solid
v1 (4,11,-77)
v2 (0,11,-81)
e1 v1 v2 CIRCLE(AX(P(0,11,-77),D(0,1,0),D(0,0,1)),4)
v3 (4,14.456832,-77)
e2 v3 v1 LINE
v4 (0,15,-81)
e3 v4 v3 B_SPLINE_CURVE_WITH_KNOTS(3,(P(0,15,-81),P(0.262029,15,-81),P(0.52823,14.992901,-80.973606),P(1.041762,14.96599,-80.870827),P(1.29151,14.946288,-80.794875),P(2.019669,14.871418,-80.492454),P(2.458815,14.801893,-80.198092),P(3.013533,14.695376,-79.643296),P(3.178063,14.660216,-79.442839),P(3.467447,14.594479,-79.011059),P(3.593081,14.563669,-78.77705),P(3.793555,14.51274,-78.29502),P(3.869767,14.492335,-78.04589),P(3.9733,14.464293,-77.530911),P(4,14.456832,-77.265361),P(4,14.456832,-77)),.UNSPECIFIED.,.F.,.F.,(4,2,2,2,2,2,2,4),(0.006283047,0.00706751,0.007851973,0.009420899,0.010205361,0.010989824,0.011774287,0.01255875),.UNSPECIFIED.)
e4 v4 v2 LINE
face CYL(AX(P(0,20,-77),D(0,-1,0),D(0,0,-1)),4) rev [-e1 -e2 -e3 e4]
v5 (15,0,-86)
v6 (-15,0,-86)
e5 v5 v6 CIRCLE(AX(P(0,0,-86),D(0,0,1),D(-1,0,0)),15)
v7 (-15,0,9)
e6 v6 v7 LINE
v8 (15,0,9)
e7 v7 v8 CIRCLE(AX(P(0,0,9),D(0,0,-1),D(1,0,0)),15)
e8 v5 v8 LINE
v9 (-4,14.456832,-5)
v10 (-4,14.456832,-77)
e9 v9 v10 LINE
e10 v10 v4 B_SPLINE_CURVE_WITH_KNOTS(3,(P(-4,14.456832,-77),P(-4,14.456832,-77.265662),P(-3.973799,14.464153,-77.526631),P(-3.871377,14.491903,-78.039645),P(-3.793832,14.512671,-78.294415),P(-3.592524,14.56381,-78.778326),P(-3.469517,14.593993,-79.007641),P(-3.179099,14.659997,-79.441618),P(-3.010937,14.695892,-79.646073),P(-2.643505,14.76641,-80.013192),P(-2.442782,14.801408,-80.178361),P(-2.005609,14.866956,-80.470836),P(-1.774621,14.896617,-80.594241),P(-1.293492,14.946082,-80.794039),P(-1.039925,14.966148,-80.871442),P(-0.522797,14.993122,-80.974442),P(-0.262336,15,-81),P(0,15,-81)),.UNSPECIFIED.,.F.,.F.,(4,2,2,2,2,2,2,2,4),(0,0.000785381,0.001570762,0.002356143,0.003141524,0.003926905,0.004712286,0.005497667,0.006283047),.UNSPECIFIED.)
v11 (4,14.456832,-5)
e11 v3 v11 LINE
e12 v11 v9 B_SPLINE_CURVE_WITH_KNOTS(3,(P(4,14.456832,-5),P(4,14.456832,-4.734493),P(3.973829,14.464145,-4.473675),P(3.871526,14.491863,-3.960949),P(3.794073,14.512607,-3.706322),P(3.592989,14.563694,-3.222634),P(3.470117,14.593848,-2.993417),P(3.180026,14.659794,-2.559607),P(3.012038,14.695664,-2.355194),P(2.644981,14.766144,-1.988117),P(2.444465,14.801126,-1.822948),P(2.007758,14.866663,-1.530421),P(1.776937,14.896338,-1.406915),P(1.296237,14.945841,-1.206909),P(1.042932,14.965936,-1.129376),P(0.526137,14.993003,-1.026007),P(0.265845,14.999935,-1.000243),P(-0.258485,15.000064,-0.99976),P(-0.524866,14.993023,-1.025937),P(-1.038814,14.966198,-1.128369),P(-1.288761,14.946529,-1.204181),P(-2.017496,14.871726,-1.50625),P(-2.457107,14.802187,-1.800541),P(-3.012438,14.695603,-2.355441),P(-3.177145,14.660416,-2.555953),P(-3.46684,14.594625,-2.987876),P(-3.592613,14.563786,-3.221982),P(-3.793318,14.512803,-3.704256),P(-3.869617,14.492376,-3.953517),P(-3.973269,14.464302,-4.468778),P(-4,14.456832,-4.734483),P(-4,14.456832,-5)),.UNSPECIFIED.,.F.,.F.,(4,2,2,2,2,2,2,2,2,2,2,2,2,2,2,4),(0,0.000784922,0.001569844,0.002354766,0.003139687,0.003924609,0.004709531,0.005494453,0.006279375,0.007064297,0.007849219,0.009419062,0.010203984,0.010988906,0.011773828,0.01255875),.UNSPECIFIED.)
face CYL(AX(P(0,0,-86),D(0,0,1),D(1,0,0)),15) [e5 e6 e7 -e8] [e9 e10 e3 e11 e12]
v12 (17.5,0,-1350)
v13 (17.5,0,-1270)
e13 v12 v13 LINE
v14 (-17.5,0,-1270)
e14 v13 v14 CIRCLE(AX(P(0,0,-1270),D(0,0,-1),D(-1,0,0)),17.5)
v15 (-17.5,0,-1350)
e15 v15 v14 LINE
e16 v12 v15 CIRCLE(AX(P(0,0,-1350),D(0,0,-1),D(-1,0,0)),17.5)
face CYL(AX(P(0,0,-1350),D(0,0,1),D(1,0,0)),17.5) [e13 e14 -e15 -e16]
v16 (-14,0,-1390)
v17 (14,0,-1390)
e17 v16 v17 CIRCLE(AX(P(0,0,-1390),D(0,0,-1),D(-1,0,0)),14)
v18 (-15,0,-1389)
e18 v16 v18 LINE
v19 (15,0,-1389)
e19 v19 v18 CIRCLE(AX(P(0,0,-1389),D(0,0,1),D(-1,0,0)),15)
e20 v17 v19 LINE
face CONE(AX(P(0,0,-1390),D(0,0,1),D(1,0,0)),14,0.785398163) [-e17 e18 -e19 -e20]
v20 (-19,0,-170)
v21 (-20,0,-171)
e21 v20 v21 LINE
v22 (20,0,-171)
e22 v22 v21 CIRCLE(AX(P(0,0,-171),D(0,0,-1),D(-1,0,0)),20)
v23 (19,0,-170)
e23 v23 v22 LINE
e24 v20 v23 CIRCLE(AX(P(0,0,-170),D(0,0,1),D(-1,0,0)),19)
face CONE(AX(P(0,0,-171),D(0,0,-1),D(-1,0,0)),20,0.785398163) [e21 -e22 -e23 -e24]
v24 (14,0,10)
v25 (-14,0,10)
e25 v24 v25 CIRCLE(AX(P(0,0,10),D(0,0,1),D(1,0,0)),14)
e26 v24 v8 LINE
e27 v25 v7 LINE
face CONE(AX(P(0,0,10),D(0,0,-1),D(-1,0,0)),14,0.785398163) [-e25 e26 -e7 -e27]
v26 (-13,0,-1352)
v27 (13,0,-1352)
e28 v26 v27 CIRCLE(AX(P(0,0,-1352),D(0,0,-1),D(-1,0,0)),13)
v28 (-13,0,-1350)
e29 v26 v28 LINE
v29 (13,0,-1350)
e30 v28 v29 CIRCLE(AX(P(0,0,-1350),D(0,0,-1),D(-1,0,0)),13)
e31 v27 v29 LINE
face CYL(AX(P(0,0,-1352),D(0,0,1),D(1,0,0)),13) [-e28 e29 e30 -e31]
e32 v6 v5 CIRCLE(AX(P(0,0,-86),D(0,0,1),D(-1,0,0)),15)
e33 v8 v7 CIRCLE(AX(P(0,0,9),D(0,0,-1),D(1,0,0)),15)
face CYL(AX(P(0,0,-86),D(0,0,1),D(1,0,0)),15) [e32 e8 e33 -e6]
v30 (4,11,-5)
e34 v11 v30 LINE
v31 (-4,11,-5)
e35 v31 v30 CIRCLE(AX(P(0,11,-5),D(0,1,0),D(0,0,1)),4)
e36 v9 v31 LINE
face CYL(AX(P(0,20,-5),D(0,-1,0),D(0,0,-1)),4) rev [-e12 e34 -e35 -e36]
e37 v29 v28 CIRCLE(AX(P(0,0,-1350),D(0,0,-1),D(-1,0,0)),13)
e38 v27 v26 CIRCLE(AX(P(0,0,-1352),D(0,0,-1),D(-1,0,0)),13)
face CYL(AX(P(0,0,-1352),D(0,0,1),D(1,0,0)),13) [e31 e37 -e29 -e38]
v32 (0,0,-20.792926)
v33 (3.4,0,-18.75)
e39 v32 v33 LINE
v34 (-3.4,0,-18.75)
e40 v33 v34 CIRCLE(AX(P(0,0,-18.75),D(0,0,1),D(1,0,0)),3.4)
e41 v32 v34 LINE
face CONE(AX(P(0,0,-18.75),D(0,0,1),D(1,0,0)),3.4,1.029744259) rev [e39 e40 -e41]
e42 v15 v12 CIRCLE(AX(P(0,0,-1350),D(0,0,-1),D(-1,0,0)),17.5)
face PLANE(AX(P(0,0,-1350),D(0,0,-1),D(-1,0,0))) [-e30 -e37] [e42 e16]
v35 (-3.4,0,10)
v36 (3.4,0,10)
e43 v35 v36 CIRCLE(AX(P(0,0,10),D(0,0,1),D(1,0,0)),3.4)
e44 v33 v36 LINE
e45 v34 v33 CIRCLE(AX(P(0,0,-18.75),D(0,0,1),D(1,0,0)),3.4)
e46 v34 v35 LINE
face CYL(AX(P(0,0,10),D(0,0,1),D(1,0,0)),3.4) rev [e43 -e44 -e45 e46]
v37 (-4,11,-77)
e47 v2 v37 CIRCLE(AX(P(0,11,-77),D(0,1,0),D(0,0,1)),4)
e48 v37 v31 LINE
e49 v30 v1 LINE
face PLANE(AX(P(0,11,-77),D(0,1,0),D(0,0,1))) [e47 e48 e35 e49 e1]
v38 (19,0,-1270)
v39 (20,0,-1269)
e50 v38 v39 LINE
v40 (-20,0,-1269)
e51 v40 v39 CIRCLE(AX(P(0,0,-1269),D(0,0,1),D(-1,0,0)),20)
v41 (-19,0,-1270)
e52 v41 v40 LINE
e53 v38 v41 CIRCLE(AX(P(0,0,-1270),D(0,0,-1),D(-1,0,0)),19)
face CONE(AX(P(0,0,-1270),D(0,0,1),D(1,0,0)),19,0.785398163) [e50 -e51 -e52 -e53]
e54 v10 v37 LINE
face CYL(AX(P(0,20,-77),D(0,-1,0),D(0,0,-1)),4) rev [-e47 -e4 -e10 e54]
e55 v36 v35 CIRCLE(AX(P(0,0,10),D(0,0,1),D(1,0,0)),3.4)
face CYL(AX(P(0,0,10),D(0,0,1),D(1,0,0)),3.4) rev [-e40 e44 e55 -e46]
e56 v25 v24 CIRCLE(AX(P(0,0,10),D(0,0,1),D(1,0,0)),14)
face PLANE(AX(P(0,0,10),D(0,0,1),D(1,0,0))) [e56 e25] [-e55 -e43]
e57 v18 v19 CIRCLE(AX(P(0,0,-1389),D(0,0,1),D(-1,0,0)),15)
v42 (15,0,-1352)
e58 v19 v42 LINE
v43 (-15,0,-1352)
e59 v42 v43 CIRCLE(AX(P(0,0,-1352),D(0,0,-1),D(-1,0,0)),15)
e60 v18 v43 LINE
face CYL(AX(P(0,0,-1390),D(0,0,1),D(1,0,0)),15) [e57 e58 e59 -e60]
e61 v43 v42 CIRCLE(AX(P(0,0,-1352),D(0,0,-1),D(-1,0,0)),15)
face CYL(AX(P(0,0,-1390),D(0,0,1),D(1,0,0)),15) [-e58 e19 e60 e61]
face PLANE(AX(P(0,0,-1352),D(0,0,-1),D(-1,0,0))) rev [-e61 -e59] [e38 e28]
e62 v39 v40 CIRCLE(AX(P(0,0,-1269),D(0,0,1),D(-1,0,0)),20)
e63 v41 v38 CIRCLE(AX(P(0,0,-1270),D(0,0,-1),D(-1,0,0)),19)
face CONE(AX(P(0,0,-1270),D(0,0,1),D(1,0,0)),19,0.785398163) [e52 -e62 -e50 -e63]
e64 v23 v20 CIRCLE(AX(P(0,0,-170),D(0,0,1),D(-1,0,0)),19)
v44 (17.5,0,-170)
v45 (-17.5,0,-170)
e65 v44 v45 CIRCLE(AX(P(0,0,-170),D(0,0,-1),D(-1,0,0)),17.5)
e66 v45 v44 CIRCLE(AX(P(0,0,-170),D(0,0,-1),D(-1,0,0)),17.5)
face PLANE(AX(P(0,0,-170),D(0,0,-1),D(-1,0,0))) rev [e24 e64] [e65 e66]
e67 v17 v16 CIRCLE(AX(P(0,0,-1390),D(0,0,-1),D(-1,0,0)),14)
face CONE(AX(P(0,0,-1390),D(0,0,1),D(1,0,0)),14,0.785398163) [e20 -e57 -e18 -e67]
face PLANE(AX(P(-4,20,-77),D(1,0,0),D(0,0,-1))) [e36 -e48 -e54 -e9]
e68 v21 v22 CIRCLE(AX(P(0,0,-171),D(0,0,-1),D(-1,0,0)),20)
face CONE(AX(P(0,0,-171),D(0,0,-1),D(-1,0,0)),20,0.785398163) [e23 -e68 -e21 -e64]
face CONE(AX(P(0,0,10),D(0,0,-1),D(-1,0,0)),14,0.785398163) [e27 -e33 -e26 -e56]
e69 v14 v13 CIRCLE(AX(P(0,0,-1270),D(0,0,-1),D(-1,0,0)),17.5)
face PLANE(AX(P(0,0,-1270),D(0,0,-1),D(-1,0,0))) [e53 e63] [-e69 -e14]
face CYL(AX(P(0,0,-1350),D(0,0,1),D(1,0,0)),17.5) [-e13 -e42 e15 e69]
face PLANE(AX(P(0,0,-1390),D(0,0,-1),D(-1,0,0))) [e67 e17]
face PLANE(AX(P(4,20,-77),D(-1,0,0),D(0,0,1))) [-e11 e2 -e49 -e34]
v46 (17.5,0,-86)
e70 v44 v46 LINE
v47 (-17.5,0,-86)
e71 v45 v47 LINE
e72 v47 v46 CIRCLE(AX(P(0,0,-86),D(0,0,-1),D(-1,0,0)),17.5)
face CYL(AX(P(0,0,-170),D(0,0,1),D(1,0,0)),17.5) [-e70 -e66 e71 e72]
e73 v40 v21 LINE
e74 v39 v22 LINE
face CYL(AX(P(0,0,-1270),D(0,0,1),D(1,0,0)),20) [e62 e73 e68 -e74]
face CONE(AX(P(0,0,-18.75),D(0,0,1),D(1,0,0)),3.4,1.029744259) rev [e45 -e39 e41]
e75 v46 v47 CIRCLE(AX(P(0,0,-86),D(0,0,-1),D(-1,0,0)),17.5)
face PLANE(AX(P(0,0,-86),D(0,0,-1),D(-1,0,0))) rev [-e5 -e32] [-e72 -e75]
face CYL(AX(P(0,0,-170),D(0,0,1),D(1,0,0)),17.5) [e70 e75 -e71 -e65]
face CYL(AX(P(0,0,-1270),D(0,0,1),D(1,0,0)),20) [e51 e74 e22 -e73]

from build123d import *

# Parameters (mm, degrees)
SKETCH_2_R             = 15
EXTRUDE_1_DEPTH        = 96
SKETCH_3_R             = 17.5
EXTRUDE_2_DEPTH        = 84
SKETCH_4_R             = 20
EXTRUDE_3_DEPTH        = 1100
SKETCH_6_R             = 17.5
EXTRUDE_4_DEPTH        = 80
SKETCH_7_R             = 13
EXTRUDE_5_DEPTH        = 2
SKETCH_9_R             = 15
EXTRUDE_6_DEPTH        = 38
CHAMFER_1_SIZE         = 1
CHAMFER_2_SIZE         = 1
CHAMFER_3_SIZE         = 1
CHAMFER_4_SIZE         = 1
HOLE_WIZARD_M8_2_D     = 6.8
HOLE_WIZARD_M8_2_DEPTH = 28.75
HOLE_WIZARD_M8_2_TIP   = 2.042926105
CUT_EXTRUDE_1_DEPTH    = 1391.489482161


with BuildPart() as part:
    # 草图2 → 凸台-拉伸1 (new body)
    with BuildSketch(Plane.XY):
        Circle(SKETCH_2_R)
    extrude(amount=-EXTRUDE_1_DEPTH)

    # 草图3 → 凸台-拉伸2 (add)
    with BuildSketch(Plane(origin=(0, 0, -96), x_dir=(-1, 0, 0), z_dir=(0, 0, -1))):
        with Locations(Location((0, 0, 0), (0, 0, 180))):
            Circle(SKETCH_3_R)
    extrude(amount=EXTRUDE_2_DEPTH)

    # 草图4 → 凸台-拉伸3 (add)
    with BuildSketch(Plane(origin=(0, 0, -180), x_dir=(-1, 0, 0), z_dir=(0, 0, -1))):
        Circle(SKETCH_4_R)
    extrude(amount=EXTRUDE_3_DEPTH)

    # 草图6 → 凸台-拉伸4 (add)
    with BuildSketch(Plane(origin=(0, 0, -1280), x_dir=(-1, 0, 0), z_dir=(0, 0, -1))):
        with Locations(Location((0, 0, 0), (0, 0, 180))):
            Circle(SKETCH_6_R)
    extrude(amount=EXTRUDE_4_DEPTH)

    # 草图7 → 凸台-拉伸5 (add)
    with BuildSketch(Plane(origin=(0, 0, -1360), x_dir=(-1, 0, 0), z_dir=(0, 0, -1))):
        Circle(SKETCH_7_R)
    extrude(amount=EXTRUDE_5_DEPTH)

    # 草图9 → 凸台-拉伸6 (add)
    with BuildSketch(Plane(origin=(0, 0, -1362), x_dir=(-1, 0, 0), z_dir=(0, 0, -1))):
        with Locations(Location((0, 0, 0), (0, 0, 180))):
            Circle(SKETCH_9_R)
    extrude(amount=EXTRUDE_6_DEPTH)

    # 倒角1
    chamfer_1_edges = [part.edges().sort_by_distance(p)[0] for p in [
        (-15, 0, -1400),
    ]]
    chamfer(chamfer_1_edges, length=CHAMFER_1_SIZE)

    # 倒角2
    chamfer_2_edges = [part.edges().sort_by_distance(p)[0] for p in [
        (20, 0, -1280),
    ]]
    chamfer(chamfer_2_edges, length=CHAMFER_2_SIZE)

    # 倒角3
    chamfer_3_edges = [part.edges().sort_by_distance(p)[0] for p in [
        (20, 0, -180),
    ]]
    chamfer(chamfer_3_edges, length=CHAMFER_3_SIZE)

    # 倒角4
    chamfer_4_edges = [part.edges().sort_by_distance(p)[0] for p in [
        (-15, 0, 0),
    ]]
    chamfer(chamfer_4_edges, length=CHAMFER_4_SIZE)


with BuildPart() as part_1:
    # Move Body 1: moved
    add(part.part.moved(Location((0, 0, 10))))

    # M8 螺纹孔2
    with Locations(Plane.XY.offset(10)):
        with Locations((0, 0)):
            Hole(HOLE_WIZARD_M8_2_D / 2, depth=HOLE_WIZARD_M8_2_DEPTH)
            with Locations((0, 0, -(HOLE_WIZARD_M8_2_DEPTH + HOLE_WIZARD_M8_2_TIP / 2))):  # 118° drill point
                Cone(0, HOLE_WIZARD_M8_2_D / 2, HOLE_WIZARD_M8_2_TIP, mode=Mode.SUBTRACT)

    # 草图18 → 切除-拉伸1 (cut, through all)
    with BuildSketch(Plane(origin=(0, 11, 0), x_dir=(1, 0, 0), z_dir=(0, 1, 0))):
        with BuildLine():
            Line((4, 77), (4, 5))
            ThreePointArc((4, 5), (0, 1), (-4, 5))
            Line((-4, 5), (-4, 77))
            ThreePointArc((-4, 77), (0, 81), (4, 77))
        make_face()
    extrude(amount=CUT_EXTRUDE_1_DEPTH, mode=Mode.SUBTRACT)


solid = part_1.part
